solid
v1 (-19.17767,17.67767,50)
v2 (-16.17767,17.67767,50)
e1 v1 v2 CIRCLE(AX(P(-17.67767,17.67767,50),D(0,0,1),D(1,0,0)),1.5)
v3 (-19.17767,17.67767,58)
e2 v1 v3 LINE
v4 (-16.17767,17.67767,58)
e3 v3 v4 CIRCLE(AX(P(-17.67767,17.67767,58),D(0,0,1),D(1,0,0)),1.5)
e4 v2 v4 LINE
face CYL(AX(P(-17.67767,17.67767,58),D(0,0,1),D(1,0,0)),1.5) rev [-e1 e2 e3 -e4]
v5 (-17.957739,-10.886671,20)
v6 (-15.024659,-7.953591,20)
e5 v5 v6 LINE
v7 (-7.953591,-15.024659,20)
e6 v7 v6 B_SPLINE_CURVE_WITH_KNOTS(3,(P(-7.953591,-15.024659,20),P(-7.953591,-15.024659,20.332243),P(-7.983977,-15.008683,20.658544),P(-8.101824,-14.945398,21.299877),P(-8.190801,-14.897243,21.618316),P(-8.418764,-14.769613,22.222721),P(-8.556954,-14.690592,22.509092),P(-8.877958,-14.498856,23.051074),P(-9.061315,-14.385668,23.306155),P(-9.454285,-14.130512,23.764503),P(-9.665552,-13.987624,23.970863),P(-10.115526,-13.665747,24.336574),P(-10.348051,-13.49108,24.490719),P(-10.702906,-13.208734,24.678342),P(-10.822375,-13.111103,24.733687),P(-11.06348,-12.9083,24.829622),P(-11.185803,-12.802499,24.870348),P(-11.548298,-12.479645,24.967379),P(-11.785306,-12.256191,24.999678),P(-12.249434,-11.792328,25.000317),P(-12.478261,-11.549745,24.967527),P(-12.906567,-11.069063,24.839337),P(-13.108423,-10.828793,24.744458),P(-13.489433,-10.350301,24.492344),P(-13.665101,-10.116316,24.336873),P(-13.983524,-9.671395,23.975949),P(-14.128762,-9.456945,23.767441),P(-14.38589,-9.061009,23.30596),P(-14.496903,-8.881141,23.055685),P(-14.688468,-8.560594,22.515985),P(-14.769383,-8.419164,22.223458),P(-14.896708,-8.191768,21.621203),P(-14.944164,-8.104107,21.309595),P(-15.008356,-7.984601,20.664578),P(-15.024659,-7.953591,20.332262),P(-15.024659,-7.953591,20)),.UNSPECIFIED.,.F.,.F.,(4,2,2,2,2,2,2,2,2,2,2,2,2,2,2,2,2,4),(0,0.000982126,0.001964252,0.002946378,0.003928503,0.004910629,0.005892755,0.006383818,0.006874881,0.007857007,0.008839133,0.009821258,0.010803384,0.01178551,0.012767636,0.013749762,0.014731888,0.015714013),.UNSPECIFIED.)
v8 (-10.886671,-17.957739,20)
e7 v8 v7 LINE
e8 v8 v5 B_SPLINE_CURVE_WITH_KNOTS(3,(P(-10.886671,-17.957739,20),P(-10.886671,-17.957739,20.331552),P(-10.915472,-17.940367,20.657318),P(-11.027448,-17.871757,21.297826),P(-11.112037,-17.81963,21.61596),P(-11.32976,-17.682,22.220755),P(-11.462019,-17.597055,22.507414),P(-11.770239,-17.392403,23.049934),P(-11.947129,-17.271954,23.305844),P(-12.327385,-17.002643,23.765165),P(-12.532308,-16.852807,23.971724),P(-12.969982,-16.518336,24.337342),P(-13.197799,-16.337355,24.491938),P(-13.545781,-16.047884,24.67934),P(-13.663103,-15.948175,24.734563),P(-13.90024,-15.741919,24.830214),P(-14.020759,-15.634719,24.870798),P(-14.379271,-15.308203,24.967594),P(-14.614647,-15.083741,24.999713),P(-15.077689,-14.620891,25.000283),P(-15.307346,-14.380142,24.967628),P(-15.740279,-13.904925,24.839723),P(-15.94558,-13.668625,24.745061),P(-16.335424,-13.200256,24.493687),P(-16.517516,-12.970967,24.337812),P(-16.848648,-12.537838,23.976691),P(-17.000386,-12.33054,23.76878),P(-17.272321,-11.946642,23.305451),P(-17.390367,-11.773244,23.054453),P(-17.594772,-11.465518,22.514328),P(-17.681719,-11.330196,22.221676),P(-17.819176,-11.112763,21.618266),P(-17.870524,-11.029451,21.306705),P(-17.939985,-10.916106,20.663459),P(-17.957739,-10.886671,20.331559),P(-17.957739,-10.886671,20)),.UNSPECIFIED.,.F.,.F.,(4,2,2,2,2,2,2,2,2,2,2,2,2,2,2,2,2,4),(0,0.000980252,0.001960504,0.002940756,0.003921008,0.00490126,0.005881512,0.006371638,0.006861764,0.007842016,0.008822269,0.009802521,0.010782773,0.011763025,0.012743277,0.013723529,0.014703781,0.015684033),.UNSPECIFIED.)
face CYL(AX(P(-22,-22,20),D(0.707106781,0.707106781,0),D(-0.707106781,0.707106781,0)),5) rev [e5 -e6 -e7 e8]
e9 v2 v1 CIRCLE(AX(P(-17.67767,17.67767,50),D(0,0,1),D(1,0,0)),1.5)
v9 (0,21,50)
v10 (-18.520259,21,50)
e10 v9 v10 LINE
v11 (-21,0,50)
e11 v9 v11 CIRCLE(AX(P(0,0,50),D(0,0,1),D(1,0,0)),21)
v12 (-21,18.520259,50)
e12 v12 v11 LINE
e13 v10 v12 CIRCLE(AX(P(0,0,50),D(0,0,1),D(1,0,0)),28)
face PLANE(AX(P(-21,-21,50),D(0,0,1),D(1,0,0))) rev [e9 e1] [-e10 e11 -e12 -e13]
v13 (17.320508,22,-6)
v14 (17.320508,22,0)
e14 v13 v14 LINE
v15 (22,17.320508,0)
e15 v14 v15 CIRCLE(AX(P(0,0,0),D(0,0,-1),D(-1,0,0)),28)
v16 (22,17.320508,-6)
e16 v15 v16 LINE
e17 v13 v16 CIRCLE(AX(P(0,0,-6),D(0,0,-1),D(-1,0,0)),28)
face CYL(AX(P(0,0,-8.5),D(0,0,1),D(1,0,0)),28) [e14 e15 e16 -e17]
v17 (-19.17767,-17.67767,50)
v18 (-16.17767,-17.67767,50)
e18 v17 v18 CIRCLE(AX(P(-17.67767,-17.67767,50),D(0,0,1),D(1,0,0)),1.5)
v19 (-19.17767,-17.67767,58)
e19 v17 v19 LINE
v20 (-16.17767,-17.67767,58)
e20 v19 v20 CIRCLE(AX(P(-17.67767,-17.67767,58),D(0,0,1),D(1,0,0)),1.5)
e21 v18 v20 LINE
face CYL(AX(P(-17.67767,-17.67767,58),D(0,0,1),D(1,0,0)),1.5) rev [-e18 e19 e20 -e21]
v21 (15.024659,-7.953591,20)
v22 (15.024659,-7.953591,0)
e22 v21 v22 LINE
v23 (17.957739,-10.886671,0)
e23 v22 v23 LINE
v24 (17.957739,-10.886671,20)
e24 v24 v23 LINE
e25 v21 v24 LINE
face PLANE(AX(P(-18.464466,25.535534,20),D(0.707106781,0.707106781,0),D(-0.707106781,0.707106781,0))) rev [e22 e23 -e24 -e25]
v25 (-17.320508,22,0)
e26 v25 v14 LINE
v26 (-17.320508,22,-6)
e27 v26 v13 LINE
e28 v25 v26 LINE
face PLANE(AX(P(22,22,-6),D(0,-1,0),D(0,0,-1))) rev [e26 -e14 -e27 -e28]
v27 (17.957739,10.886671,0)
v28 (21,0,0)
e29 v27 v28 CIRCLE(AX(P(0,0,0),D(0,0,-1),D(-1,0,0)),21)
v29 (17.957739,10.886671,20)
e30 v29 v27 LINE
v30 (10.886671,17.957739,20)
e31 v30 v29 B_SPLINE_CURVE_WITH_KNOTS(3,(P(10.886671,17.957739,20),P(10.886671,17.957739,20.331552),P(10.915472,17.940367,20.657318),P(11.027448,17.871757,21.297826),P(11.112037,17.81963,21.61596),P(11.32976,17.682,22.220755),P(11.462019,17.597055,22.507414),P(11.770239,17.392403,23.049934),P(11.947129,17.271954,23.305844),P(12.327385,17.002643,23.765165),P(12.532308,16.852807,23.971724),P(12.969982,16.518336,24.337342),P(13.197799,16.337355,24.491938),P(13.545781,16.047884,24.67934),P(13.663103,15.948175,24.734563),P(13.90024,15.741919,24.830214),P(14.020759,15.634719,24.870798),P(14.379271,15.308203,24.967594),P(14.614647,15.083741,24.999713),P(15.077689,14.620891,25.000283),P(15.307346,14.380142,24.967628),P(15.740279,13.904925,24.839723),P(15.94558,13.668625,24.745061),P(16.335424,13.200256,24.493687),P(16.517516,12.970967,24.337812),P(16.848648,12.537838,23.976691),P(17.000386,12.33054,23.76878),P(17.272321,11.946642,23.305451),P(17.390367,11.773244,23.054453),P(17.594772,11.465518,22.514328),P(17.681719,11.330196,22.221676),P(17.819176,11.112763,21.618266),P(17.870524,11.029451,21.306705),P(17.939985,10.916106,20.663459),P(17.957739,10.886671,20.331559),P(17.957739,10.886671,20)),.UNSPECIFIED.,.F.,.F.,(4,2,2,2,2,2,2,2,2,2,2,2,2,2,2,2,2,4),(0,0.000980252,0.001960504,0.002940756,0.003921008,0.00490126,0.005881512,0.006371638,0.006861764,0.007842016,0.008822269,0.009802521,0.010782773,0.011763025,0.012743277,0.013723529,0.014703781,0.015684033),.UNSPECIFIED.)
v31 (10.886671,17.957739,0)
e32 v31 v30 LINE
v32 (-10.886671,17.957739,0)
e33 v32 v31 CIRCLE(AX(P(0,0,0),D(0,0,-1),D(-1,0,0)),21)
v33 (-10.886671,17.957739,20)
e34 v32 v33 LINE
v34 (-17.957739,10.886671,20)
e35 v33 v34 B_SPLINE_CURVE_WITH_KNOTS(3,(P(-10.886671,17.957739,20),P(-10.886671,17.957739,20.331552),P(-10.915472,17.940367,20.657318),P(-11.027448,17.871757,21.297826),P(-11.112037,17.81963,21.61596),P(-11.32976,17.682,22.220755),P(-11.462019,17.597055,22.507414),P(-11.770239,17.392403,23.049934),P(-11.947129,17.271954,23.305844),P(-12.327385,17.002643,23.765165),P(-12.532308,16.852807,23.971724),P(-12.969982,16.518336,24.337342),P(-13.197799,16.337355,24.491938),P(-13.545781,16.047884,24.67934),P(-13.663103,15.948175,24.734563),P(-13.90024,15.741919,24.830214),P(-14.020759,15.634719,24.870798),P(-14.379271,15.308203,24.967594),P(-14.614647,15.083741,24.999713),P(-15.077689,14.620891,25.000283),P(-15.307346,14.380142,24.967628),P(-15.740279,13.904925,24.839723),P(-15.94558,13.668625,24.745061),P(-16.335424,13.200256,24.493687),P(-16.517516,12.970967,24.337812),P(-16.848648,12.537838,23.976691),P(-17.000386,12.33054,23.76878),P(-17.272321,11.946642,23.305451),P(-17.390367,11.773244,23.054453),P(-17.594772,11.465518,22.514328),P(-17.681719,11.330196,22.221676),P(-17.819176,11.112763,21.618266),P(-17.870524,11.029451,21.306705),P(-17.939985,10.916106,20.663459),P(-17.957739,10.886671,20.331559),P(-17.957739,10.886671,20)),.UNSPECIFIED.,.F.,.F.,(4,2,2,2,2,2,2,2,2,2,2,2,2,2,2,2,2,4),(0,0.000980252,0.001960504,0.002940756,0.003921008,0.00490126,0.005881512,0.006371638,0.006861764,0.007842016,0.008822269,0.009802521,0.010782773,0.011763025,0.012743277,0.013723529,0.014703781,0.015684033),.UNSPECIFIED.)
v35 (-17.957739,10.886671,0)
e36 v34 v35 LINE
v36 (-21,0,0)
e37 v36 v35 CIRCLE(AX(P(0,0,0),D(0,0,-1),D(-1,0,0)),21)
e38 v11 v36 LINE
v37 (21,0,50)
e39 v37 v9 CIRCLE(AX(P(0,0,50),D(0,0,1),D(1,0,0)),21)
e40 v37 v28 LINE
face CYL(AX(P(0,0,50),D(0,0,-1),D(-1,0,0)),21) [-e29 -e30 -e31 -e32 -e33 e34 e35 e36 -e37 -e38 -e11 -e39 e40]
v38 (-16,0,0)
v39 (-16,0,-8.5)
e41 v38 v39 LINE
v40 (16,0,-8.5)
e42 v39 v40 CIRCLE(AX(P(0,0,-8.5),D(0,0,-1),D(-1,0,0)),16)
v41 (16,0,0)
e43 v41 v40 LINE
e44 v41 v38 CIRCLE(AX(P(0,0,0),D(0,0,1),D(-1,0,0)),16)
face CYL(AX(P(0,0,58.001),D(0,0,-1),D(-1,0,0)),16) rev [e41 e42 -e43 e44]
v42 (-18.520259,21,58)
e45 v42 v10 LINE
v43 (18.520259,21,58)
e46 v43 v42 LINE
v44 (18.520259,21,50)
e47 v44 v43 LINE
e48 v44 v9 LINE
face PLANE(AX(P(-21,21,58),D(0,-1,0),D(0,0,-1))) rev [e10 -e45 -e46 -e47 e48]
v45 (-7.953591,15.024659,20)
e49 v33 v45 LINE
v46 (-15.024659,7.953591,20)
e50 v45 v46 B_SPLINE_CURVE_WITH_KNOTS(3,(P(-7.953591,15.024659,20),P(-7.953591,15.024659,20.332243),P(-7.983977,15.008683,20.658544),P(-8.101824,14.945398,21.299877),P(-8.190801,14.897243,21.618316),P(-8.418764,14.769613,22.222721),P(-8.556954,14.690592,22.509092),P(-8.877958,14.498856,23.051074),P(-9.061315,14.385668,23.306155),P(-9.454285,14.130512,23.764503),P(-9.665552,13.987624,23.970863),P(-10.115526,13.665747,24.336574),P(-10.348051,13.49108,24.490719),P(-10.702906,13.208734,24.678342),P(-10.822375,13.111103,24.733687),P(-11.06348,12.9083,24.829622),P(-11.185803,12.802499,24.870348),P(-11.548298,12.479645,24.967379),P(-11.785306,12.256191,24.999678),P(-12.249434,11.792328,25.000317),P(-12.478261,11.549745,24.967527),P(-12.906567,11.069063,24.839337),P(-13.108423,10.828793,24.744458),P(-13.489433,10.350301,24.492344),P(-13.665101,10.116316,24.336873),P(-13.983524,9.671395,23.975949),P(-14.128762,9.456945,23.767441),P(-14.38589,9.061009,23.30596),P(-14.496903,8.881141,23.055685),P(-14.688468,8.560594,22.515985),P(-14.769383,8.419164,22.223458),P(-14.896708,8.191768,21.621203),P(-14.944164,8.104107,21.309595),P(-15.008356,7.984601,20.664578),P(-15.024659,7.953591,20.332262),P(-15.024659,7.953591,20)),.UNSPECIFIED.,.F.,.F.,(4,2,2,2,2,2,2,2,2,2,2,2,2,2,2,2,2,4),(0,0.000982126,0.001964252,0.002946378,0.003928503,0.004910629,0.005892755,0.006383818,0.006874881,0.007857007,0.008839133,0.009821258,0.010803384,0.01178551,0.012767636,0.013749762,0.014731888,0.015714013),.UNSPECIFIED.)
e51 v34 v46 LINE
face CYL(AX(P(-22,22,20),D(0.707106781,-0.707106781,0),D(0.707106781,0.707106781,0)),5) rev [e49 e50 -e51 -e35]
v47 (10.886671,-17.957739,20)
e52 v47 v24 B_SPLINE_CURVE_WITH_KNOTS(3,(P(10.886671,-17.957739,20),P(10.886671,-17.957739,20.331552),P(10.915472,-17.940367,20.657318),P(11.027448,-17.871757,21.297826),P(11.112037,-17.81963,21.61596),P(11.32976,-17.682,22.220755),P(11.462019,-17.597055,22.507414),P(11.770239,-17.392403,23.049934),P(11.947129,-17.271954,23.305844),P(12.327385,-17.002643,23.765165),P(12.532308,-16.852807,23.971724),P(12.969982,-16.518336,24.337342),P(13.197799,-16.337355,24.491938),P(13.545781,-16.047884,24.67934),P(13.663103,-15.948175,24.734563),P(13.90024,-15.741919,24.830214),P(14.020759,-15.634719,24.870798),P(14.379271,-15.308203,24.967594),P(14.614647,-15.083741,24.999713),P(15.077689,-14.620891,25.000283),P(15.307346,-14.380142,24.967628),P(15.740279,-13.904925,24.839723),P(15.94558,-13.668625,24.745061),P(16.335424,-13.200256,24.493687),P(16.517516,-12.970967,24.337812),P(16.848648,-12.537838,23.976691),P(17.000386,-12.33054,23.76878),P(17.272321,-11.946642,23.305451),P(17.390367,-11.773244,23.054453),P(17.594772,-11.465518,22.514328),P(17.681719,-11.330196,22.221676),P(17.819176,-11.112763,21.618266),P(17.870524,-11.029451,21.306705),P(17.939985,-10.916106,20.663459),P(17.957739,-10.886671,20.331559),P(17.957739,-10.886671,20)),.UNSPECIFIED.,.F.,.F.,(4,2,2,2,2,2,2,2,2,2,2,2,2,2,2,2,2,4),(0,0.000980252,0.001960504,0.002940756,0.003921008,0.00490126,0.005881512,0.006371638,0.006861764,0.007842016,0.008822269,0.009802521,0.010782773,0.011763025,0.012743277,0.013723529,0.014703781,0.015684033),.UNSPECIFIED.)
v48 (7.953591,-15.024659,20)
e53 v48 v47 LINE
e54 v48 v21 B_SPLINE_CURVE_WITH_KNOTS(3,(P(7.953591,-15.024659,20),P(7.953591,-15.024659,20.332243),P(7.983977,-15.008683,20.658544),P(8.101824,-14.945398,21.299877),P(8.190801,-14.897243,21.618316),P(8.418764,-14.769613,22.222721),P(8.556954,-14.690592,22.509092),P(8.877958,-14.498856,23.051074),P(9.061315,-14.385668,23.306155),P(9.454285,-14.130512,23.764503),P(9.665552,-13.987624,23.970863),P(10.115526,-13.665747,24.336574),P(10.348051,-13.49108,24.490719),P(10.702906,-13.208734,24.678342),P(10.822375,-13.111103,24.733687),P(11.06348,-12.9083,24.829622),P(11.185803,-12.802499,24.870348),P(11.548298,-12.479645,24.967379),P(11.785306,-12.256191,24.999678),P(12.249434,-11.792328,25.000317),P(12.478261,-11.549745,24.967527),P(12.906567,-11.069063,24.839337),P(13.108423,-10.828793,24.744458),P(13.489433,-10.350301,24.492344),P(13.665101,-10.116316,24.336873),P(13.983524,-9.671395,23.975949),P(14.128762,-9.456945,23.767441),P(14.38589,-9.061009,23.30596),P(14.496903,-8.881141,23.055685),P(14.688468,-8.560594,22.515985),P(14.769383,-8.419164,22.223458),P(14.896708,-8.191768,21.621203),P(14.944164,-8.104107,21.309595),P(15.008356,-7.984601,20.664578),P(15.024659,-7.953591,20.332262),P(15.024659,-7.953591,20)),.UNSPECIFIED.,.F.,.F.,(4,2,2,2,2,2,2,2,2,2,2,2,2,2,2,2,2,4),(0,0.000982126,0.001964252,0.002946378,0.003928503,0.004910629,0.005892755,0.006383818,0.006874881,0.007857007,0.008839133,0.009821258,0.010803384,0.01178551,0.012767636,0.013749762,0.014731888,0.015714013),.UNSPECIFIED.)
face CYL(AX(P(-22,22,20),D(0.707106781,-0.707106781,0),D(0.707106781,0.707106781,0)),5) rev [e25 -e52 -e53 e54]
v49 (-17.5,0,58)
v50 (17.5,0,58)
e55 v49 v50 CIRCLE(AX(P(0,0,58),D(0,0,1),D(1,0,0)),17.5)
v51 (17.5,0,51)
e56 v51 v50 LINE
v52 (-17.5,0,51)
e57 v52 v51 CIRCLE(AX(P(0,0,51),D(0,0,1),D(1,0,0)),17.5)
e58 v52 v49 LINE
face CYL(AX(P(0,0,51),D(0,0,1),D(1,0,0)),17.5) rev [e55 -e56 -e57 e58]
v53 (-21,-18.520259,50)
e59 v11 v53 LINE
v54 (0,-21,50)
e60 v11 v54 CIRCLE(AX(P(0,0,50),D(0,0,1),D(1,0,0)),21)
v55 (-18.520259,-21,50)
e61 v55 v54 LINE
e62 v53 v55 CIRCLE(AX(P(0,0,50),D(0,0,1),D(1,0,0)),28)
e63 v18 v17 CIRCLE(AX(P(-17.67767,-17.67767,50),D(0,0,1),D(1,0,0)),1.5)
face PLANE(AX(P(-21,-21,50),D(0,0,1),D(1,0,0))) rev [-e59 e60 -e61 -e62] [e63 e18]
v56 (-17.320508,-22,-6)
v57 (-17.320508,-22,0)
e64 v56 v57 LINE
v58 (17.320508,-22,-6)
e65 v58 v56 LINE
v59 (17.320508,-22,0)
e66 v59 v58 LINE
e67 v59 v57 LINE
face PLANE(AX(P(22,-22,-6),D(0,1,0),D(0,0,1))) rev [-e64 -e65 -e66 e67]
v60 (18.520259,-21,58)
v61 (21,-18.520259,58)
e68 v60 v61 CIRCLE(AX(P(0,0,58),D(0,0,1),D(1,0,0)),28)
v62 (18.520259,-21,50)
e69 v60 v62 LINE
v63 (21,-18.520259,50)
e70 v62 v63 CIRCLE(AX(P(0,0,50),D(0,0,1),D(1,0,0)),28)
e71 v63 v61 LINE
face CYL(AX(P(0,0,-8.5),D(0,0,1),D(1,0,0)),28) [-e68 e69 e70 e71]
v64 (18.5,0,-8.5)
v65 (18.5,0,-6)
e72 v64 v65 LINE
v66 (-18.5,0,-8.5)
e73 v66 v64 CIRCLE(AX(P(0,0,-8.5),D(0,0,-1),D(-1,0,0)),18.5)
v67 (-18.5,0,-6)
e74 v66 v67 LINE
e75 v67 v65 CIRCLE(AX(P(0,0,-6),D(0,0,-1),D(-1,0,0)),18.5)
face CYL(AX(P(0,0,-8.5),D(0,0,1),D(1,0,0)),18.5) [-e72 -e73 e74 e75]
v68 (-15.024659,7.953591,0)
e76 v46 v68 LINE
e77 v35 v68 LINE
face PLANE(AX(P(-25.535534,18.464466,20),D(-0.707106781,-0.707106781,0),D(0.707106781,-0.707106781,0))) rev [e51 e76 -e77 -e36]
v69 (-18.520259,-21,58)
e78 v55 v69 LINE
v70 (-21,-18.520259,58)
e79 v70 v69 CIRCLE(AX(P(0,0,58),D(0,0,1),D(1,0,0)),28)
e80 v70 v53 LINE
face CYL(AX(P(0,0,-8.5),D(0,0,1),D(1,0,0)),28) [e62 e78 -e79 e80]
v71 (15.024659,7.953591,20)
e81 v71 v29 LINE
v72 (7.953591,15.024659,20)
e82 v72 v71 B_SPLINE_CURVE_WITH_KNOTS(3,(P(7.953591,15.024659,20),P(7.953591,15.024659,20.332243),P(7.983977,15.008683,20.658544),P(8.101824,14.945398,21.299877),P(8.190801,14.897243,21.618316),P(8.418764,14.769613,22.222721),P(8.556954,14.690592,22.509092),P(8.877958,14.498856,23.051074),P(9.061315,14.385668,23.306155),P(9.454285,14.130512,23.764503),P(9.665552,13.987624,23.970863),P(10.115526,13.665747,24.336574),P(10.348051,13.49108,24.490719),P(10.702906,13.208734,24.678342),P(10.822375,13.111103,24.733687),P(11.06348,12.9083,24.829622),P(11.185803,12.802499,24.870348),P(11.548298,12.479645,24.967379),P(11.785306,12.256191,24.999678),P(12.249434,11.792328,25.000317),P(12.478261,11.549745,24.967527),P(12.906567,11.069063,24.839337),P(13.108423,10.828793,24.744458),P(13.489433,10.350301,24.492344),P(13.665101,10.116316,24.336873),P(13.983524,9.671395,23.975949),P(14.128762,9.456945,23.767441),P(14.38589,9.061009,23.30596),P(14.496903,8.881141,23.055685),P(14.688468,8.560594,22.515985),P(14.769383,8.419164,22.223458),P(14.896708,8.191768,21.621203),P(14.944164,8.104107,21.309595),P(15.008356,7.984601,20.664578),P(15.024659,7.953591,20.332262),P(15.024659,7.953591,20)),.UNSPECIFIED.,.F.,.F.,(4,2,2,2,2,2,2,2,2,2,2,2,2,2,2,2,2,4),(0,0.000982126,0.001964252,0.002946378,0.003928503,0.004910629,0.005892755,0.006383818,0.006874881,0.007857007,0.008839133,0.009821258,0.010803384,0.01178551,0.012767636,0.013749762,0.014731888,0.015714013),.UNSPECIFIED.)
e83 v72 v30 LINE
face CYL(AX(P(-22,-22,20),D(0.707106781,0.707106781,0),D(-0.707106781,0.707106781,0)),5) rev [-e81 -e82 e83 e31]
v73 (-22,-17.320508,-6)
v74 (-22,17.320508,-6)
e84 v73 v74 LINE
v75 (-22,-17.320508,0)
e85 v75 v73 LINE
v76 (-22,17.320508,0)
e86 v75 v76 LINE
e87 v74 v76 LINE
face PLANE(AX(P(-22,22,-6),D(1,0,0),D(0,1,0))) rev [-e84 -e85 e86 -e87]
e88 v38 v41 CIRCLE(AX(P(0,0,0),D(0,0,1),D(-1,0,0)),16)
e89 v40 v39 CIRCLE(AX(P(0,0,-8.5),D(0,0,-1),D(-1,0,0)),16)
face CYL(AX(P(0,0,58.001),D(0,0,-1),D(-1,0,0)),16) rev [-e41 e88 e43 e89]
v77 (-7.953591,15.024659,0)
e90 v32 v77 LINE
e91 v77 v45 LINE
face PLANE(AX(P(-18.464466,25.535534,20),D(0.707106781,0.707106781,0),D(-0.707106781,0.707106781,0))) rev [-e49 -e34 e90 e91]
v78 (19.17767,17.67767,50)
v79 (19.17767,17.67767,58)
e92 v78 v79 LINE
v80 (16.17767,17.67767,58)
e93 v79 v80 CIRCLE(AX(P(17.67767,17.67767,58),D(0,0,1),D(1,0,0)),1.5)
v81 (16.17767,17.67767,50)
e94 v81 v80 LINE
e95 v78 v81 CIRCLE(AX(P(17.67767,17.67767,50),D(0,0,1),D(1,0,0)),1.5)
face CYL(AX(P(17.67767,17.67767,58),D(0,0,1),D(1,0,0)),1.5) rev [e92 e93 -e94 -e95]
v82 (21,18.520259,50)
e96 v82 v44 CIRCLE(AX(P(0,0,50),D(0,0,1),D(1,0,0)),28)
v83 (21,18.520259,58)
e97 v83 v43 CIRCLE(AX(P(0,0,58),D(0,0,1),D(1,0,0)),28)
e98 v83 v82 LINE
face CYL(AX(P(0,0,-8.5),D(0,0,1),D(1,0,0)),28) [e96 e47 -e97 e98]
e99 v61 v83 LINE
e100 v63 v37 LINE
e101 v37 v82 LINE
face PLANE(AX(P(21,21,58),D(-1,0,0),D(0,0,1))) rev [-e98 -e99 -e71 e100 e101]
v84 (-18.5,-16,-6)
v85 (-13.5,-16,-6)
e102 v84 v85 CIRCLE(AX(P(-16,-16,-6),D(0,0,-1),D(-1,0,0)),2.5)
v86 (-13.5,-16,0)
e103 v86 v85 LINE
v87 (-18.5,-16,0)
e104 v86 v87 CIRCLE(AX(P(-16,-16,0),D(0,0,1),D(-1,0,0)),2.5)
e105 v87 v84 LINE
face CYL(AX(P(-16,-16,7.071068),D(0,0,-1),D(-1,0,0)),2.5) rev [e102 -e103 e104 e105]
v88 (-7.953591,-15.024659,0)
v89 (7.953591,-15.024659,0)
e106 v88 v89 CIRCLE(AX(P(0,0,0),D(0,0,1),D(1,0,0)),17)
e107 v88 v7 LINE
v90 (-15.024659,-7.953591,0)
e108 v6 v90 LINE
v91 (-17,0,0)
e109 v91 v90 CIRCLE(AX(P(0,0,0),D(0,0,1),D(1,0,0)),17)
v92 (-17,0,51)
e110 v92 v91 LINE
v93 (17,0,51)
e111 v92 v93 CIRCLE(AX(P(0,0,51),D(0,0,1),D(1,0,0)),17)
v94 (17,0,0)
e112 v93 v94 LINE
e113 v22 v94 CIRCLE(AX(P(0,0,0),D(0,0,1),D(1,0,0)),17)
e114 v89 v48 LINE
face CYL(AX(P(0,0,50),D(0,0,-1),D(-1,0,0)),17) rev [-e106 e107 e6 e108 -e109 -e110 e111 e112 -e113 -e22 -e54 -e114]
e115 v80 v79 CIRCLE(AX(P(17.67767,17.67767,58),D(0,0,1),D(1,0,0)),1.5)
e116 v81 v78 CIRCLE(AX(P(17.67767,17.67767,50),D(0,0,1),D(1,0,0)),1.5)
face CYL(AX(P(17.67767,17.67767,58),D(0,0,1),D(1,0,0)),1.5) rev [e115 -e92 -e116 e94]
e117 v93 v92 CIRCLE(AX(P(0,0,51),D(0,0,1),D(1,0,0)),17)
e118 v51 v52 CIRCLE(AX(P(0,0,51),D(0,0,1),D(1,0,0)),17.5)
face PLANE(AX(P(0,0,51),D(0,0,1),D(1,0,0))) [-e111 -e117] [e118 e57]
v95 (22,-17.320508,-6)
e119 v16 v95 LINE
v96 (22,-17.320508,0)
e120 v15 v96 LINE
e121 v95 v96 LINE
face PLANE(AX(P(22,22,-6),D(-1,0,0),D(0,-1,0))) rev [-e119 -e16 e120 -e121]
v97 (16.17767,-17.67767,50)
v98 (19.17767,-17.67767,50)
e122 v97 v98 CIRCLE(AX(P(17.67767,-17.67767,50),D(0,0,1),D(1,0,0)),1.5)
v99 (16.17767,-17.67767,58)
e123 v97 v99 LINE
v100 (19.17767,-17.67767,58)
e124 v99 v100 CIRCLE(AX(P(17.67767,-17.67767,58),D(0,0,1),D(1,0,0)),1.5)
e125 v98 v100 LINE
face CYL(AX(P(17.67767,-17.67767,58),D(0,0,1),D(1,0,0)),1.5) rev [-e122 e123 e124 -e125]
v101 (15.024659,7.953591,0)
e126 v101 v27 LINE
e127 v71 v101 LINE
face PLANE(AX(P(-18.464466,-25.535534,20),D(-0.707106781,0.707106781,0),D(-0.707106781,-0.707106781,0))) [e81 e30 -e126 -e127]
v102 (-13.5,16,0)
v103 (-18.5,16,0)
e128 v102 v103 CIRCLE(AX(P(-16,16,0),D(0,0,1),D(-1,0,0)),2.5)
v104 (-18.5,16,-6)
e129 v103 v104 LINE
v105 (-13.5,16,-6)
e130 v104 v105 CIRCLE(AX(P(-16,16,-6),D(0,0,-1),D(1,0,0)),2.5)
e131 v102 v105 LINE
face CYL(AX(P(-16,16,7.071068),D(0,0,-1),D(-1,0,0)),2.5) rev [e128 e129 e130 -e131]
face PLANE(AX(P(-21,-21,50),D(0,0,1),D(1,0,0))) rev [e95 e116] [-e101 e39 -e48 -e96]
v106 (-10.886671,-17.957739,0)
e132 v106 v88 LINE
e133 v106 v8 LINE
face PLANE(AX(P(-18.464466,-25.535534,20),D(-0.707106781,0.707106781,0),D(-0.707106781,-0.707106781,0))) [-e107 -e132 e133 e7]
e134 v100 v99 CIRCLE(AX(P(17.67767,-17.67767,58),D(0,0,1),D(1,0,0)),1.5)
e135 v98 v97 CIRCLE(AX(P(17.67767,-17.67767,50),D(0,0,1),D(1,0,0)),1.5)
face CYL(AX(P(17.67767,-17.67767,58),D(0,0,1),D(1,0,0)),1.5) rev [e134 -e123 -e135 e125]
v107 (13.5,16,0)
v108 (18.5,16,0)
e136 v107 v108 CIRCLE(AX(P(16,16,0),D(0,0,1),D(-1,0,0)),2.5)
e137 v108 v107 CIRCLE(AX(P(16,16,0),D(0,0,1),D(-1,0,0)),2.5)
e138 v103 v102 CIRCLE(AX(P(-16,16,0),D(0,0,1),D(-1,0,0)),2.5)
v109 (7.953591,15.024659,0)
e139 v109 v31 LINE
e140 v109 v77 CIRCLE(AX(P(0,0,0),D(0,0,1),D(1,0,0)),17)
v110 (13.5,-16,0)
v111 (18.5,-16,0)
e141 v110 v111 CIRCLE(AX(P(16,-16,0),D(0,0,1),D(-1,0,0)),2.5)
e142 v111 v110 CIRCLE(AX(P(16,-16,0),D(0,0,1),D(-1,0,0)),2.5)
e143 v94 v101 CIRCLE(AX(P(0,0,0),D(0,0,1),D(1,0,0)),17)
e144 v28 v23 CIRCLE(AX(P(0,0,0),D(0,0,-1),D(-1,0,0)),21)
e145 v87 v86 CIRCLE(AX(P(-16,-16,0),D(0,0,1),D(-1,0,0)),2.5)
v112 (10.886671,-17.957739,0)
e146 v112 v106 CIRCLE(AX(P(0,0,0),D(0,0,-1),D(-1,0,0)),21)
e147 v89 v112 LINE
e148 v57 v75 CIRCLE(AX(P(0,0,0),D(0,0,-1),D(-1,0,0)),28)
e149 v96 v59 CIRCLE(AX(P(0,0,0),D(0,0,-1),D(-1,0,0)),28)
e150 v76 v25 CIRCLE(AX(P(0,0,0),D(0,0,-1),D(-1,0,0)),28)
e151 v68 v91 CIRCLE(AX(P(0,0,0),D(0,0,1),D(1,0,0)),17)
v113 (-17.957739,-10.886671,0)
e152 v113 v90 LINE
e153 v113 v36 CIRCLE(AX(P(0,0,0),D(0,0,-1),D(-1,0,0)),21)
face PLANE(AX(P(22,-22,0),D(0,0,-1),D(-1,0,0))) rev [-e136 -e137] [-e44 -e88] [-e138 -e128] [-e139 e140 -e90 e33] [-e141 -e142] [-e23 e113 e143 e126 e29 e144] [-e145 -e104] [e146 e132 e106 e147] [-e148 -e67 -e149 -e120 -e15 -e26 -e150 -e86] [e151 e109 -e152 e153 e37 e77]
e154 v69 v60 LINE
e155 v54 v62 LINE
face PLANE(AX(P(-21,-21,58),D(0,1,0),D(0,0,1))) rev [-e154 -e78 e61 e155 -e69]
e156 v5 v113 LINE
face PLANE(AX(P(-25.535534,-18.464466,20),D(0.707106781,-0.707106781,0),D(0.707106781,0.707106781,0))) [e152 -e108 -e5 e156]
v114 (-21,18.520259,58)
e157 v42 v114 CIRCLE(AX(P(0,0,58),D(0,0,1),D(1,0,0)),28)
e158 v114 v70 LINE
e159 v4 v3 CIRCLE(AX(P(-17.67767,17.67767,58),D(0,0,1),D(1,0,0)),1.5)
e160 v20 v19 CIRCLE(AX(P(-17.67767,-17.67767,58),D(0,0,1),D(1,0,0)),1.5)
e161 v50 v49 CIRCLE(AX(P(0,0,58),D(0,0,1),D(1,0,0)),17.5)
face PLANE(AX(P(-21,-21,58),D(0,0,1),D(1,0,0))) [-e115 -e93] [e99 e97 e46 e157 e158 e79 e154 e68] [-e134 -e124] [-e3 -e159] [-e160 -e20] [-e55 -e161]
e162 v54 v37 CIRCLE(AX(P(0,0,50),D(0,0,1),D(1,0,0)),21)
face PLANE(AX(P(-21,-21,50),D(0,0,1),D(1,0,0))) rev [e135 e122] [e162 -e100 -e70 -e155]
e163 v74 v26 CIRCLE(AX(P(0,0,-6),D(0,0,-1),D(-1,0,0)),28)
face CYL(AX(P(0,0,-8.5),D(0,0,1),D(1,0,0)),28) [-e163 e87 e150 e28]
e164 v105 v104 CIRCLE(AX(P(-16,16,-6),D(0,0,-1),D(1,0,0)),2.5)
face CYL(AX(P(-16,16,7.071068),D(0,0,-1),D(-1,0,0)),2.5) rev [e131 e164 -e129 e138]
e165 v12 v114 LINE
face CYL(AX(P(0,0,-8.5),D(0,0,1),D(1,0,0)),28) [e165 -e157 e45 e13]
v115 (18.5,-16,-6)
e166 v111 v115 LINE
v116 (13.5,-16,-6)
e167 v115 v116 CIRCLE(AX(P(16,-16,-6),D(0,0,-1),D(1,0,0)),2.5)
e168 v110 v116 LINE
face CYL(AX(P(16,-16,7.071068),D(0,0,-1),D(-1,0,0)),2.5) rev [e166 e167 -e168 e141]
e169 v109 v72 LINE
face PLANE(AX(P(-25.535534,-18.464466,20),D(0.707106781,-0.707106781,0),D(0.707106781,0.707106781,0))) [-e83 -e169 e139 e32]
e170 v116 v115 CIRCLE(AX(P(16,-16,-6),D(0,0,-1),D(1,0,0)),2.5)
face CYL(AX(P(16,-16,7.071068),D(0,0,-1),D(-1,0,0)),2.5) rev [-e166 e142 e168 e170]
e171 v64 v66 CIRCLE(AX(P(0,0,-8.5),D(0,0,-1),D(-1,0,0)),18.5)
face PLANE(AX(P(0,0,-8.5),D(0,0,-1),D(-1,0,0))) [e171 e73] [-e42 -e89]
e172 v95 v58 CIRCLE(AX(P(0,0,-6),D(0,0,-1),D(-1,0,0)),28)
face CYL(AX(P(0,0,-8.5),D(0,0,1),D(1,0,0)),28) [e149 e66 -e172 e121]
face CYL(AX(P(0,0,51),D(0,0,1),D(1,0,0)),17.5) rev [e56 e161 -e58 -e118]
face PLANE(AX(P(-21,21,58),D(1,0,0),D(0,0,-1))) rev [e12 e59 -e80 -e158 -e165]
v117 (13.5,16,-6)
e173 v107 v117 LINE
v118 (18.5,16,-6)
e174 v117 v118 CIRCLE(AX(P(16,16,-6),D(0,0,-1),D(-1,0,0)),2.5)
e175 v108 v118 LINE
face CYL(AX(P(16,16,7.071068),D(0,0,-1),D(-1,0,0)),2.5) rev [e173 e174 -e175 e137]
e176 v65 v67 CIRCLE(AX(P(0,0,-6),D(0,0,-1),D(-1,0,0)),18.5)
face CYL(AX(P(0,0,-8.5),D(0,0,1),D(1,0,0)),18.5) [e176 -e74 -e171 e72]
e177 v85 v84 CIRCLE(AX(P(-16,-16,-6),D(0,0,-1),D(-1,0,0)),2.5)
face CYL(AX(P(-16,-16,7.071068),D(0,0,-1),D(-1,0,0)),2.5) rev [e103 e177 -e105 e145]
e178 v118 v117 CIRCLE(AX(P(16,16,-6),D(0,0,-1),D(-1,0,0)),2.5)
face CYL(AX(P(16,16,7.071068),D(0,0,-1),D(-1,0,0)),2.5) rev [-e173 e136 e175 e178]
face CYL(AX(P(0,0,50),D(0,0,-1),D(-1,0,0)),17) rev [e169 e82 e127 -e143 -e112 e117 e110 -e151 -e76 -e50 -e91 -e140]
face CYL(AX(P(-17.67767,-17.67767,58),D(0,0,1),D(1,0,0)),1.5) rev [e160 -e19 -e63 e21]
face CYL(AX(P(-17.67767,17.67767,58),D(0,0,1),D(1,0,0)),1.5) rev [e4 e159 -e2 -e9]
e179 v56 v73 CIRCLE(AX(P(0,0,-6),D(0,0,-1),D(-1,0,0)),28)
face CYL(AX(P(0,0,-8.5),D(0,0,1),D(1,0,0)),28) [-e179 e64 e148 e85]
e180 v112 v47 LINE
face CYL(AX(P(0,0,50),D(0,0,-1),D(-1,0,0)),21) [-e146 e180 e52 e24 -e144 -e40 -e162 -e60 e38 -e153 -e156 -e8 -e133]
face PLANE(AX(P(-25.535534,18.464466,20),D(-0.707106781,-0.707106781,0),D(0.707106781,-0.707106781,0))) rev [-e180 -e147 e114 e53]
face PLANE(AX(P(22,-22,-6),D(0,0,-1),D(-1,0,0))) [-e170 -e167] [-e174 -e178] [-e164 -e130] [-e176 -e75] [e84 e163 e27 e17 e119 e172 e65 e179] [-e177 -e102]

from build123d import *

# Parameters (mm, degrees)
SKETCH_1_R           = 21
SKETCH_1_R_2         = 17
EXTRUDE_1_DEPTH      = 50
SKETCH_3_W           = 44
SKETCH_3_H           = 44
EXTRUDE_2_DEPTH      = 6
SKETCH_4_R           = 2.5
CUT_EXTRUDE_2_DEPTH  = 6
SKETCH_5_W           = 42
SKETCH_5_H           = 42
EXTRUDE_3_DEPTH      = 8
SKETCH_6_R           = 18.5
EXTRUDE_4_DEPTH      = 2.5
CUT_EXTRUDE_3_REACH  = 75.418
SKETCH_7_R           = 17
SKETCH_8_R           = 17.5
CUT_EXTRUDE_4_DEPTH  = 7
M3X0_5_1_D           = 2.5
M3X0_5_1_DEPTH       = 9.5
M3X0_5_1_CBORE_D     = 3
M3X0_5_1_CBORE_DEPTH = 8
M3X0_5_1_TIP         = 0.751075774
CUT_EXTRUDE_6_DEPTH  = 91.112429775
CUT_EXTRUDE_7_DEPTH  = 91.112429775
CUT_EXTRUDE_8_REACH  = 75.418
SKETCH_13_R          = 16
SKETCH_14_OUTSIDE_W  = 64.214
SKETCH_14_OUTSIDE_H  = 64.214
SKETCH_14_OUTSIDE_R  = 28
CUT_EXTRUDE_9_DEPTH  = 74.418321964


with BuildPart() as part:
    # 草图1 → 拉伸1 (new body)
    with BuildSketch(Plane.XY):
        Circle(SKETCH_1_R)
        Circle(SKETCH_1_R_2, mode=Mode.SUBTRACT)
    extrude(amount=EXTRUDE_1_DEPTH)

    # 草图3 → 拉伸2 (add)
    with BuildSketch(Plane(origin=(0, 0, 0), x_dir=(-1, 0, 0), z_dir=(0, 0, -1))):
        Rectangle(SKETCH_3_W, SKETCH_3_H)
    extrude(amount=EXTRUDE_2_DEPTH)

    # 草图4 → 切除-拉伸2 (cut)
    with BuildSketch(Plane(origin=(0, 0, -6), x_dir=(-1, 0, 0), z_dir=(0, 0, -1))):
        with Locations((-16, 16)):
            Circle(SKETCH_4_R)
        with Locations(Location((16, 16, 0), (0, 0, 271.937166839))):
            Circle(SKETCH_4_R)
        with Locations((16, -16)):
            Circle(SKETCH_4_R)
        with Locations(Location((-16, -16, 0), (0, 0, 358.062833161))):
            Circle(SKETCH_4_R)
    extrude(amount=-CUT_EXTRUDE_2_DEPTH, mode=Mode.SUBTRACT)

    # 草图5 → 拉伸3 (add)
    with BuildSketch(Plane.XY.offset(50)):
        Rectangle(SKETCH_5_W, SKETCH_5_H)
    extrude(amount=EXTRUDE_3_DEPTH)

    # 草图6 → 拉伸4 (add)
    with BuildSketch(Plane(origin=(0, 0, -6), x_dir=(-1, 0, 0), z_dir=(0, 0, -1))):
        Circle(SKETCH_6_R)
    extrude(amount=EXTRUDE_4_DEPTH)

    # 草图7 → 切除-拉伸3 (cut, up to next)
    with BuildSketch(Plane.XY.offset(58), mode=Mode.PRIVATE) as cut_extrude_3_sk1:
        Circle(SKETCH_7_R)
    cut_extrude_3_tool1 = extrude(cut_extrude_3_sk1.sketch, amount=-CUT_EXTRUDE_3_REACH, mode=Mode.PRIVATE) & part.part
    add(cut_extrude_3_tool1.solids().sort_by_distance((0, 0, 58))[0], mode=Mode.SUBTRACT)

    # 草图8 → 切除-拉伸4 (cut)
    with BuildSketch(Plane.XY.offset(58)):
        Circle(SKETCH_8_R)
    extrude(amount=-CUT_EXTRUDE_4_DEPTH, mode=Mode.SUBTRACT)

    # M3x0.5 螺纹孔1
    with Locations(Plane(origin=(-17.67766953, 17.67766953, 58), x_dir=(1, 0, 0), z_dir=(0, 0, 1))):
        with Locations((0, 0), (35.35533906, 0), (0, -35.35533906), (35.35533906, -35.35533906)):
            CounterBoreHole(M3X0_5_1_D / 2, M3X0_5_1_CBORE_D / 2, M3X0_5_1_CBORE_DEPTH, depth=M3X0_5_1_DEPTH)
            with Locations((0, 0, -(M3X0_5_1_DEPTH + M3X0_5_1_TIP / 2))):  # 118° drill point
                Cone(0, M3X0_5_1_D / 2, M3X0_5_1_TIP, mode=Mode.SUBTRACT)

    # 草图11 → 切除-拉伸6 (cut, through all)
    with BuildSketch(Plane(origin=(21, 21, 58), x_dir=(0.7071067811865475, -0.7071067811865477, 0), z_dir=(-0.7071067811865477, -0.7071067811865475, 0))):
        with BuildLine():
            Line((-5, -38), (-5, -58))
            Line((-5, -58), (5, -58))
            Line((5, -58), (5, -38))
            ThreePointArc((5, -38), (0, -33), (-5, -38))
        make_face()
    extrude(amount=CUT_EXTRUDE_6_DEPTH, mode=Mode.SUBTRACT)

    # 草图12 → 切除-拉伸7 (cut, through all)
    with BuildSketch(Plane(origin=(21, -21, 58), x_dir=(0.7071067811865475, 0.7071067811865477, 0), z_dir=(0.7071067811865477, -0.7071067811865475, 0))):
        with BuildLine():
            Line((-5, -38), (-5, -58))
            Line((-5, -58), (5, -58))
            Line((5, -58), (5, -38))
            ThreePointArc((5, -38), (0, -33), (-5, -38))
        make_face()
    extrude(amount=-CUT_EXTRUDE_7_DEPTH, mode=Mode.SUBTRACT)

    # 草图13 → 切除-拉伸8 (cut, up to next)
    with BuildSketch(Plane(origin=(0, 0, -8.5), x_dir=(-1, 0, 0), z_dir=(0, 0, -1)), mode=Mode.PRIVATE) as cut_extrude_8_sk1:
        Circle(SKETCH_13_R)
    cut_extrude_8_tool1 = extrude(cut_extrude_8_sk1.sketch, amount=-CUT_EXTRUDE_8_REACH, mode=Mode.PRIVATE) & part.part
    add(cut_extrude_8_tool1.solids().sort_by_distance((0, 0, -8.5))[0], mode=Mode.SUBTRACT)

    # 草图14 outside → 切除-拉伸9 (cut, through all)
    with BuildSketch(Plane.XY.offset(58)):
        Rectangle(SKETCH_14_OUTSIDE_W, SKETCH_14_OUTSIDE_H)
        Circle(SKETCH_14_OUTSIDE_R, mode=Mode.SUBTRACT)
    extrude(amount=-CUT_EXTRUDE_9_DEPTH, mode=Mode.SUBTRACT)


solid = part.part
